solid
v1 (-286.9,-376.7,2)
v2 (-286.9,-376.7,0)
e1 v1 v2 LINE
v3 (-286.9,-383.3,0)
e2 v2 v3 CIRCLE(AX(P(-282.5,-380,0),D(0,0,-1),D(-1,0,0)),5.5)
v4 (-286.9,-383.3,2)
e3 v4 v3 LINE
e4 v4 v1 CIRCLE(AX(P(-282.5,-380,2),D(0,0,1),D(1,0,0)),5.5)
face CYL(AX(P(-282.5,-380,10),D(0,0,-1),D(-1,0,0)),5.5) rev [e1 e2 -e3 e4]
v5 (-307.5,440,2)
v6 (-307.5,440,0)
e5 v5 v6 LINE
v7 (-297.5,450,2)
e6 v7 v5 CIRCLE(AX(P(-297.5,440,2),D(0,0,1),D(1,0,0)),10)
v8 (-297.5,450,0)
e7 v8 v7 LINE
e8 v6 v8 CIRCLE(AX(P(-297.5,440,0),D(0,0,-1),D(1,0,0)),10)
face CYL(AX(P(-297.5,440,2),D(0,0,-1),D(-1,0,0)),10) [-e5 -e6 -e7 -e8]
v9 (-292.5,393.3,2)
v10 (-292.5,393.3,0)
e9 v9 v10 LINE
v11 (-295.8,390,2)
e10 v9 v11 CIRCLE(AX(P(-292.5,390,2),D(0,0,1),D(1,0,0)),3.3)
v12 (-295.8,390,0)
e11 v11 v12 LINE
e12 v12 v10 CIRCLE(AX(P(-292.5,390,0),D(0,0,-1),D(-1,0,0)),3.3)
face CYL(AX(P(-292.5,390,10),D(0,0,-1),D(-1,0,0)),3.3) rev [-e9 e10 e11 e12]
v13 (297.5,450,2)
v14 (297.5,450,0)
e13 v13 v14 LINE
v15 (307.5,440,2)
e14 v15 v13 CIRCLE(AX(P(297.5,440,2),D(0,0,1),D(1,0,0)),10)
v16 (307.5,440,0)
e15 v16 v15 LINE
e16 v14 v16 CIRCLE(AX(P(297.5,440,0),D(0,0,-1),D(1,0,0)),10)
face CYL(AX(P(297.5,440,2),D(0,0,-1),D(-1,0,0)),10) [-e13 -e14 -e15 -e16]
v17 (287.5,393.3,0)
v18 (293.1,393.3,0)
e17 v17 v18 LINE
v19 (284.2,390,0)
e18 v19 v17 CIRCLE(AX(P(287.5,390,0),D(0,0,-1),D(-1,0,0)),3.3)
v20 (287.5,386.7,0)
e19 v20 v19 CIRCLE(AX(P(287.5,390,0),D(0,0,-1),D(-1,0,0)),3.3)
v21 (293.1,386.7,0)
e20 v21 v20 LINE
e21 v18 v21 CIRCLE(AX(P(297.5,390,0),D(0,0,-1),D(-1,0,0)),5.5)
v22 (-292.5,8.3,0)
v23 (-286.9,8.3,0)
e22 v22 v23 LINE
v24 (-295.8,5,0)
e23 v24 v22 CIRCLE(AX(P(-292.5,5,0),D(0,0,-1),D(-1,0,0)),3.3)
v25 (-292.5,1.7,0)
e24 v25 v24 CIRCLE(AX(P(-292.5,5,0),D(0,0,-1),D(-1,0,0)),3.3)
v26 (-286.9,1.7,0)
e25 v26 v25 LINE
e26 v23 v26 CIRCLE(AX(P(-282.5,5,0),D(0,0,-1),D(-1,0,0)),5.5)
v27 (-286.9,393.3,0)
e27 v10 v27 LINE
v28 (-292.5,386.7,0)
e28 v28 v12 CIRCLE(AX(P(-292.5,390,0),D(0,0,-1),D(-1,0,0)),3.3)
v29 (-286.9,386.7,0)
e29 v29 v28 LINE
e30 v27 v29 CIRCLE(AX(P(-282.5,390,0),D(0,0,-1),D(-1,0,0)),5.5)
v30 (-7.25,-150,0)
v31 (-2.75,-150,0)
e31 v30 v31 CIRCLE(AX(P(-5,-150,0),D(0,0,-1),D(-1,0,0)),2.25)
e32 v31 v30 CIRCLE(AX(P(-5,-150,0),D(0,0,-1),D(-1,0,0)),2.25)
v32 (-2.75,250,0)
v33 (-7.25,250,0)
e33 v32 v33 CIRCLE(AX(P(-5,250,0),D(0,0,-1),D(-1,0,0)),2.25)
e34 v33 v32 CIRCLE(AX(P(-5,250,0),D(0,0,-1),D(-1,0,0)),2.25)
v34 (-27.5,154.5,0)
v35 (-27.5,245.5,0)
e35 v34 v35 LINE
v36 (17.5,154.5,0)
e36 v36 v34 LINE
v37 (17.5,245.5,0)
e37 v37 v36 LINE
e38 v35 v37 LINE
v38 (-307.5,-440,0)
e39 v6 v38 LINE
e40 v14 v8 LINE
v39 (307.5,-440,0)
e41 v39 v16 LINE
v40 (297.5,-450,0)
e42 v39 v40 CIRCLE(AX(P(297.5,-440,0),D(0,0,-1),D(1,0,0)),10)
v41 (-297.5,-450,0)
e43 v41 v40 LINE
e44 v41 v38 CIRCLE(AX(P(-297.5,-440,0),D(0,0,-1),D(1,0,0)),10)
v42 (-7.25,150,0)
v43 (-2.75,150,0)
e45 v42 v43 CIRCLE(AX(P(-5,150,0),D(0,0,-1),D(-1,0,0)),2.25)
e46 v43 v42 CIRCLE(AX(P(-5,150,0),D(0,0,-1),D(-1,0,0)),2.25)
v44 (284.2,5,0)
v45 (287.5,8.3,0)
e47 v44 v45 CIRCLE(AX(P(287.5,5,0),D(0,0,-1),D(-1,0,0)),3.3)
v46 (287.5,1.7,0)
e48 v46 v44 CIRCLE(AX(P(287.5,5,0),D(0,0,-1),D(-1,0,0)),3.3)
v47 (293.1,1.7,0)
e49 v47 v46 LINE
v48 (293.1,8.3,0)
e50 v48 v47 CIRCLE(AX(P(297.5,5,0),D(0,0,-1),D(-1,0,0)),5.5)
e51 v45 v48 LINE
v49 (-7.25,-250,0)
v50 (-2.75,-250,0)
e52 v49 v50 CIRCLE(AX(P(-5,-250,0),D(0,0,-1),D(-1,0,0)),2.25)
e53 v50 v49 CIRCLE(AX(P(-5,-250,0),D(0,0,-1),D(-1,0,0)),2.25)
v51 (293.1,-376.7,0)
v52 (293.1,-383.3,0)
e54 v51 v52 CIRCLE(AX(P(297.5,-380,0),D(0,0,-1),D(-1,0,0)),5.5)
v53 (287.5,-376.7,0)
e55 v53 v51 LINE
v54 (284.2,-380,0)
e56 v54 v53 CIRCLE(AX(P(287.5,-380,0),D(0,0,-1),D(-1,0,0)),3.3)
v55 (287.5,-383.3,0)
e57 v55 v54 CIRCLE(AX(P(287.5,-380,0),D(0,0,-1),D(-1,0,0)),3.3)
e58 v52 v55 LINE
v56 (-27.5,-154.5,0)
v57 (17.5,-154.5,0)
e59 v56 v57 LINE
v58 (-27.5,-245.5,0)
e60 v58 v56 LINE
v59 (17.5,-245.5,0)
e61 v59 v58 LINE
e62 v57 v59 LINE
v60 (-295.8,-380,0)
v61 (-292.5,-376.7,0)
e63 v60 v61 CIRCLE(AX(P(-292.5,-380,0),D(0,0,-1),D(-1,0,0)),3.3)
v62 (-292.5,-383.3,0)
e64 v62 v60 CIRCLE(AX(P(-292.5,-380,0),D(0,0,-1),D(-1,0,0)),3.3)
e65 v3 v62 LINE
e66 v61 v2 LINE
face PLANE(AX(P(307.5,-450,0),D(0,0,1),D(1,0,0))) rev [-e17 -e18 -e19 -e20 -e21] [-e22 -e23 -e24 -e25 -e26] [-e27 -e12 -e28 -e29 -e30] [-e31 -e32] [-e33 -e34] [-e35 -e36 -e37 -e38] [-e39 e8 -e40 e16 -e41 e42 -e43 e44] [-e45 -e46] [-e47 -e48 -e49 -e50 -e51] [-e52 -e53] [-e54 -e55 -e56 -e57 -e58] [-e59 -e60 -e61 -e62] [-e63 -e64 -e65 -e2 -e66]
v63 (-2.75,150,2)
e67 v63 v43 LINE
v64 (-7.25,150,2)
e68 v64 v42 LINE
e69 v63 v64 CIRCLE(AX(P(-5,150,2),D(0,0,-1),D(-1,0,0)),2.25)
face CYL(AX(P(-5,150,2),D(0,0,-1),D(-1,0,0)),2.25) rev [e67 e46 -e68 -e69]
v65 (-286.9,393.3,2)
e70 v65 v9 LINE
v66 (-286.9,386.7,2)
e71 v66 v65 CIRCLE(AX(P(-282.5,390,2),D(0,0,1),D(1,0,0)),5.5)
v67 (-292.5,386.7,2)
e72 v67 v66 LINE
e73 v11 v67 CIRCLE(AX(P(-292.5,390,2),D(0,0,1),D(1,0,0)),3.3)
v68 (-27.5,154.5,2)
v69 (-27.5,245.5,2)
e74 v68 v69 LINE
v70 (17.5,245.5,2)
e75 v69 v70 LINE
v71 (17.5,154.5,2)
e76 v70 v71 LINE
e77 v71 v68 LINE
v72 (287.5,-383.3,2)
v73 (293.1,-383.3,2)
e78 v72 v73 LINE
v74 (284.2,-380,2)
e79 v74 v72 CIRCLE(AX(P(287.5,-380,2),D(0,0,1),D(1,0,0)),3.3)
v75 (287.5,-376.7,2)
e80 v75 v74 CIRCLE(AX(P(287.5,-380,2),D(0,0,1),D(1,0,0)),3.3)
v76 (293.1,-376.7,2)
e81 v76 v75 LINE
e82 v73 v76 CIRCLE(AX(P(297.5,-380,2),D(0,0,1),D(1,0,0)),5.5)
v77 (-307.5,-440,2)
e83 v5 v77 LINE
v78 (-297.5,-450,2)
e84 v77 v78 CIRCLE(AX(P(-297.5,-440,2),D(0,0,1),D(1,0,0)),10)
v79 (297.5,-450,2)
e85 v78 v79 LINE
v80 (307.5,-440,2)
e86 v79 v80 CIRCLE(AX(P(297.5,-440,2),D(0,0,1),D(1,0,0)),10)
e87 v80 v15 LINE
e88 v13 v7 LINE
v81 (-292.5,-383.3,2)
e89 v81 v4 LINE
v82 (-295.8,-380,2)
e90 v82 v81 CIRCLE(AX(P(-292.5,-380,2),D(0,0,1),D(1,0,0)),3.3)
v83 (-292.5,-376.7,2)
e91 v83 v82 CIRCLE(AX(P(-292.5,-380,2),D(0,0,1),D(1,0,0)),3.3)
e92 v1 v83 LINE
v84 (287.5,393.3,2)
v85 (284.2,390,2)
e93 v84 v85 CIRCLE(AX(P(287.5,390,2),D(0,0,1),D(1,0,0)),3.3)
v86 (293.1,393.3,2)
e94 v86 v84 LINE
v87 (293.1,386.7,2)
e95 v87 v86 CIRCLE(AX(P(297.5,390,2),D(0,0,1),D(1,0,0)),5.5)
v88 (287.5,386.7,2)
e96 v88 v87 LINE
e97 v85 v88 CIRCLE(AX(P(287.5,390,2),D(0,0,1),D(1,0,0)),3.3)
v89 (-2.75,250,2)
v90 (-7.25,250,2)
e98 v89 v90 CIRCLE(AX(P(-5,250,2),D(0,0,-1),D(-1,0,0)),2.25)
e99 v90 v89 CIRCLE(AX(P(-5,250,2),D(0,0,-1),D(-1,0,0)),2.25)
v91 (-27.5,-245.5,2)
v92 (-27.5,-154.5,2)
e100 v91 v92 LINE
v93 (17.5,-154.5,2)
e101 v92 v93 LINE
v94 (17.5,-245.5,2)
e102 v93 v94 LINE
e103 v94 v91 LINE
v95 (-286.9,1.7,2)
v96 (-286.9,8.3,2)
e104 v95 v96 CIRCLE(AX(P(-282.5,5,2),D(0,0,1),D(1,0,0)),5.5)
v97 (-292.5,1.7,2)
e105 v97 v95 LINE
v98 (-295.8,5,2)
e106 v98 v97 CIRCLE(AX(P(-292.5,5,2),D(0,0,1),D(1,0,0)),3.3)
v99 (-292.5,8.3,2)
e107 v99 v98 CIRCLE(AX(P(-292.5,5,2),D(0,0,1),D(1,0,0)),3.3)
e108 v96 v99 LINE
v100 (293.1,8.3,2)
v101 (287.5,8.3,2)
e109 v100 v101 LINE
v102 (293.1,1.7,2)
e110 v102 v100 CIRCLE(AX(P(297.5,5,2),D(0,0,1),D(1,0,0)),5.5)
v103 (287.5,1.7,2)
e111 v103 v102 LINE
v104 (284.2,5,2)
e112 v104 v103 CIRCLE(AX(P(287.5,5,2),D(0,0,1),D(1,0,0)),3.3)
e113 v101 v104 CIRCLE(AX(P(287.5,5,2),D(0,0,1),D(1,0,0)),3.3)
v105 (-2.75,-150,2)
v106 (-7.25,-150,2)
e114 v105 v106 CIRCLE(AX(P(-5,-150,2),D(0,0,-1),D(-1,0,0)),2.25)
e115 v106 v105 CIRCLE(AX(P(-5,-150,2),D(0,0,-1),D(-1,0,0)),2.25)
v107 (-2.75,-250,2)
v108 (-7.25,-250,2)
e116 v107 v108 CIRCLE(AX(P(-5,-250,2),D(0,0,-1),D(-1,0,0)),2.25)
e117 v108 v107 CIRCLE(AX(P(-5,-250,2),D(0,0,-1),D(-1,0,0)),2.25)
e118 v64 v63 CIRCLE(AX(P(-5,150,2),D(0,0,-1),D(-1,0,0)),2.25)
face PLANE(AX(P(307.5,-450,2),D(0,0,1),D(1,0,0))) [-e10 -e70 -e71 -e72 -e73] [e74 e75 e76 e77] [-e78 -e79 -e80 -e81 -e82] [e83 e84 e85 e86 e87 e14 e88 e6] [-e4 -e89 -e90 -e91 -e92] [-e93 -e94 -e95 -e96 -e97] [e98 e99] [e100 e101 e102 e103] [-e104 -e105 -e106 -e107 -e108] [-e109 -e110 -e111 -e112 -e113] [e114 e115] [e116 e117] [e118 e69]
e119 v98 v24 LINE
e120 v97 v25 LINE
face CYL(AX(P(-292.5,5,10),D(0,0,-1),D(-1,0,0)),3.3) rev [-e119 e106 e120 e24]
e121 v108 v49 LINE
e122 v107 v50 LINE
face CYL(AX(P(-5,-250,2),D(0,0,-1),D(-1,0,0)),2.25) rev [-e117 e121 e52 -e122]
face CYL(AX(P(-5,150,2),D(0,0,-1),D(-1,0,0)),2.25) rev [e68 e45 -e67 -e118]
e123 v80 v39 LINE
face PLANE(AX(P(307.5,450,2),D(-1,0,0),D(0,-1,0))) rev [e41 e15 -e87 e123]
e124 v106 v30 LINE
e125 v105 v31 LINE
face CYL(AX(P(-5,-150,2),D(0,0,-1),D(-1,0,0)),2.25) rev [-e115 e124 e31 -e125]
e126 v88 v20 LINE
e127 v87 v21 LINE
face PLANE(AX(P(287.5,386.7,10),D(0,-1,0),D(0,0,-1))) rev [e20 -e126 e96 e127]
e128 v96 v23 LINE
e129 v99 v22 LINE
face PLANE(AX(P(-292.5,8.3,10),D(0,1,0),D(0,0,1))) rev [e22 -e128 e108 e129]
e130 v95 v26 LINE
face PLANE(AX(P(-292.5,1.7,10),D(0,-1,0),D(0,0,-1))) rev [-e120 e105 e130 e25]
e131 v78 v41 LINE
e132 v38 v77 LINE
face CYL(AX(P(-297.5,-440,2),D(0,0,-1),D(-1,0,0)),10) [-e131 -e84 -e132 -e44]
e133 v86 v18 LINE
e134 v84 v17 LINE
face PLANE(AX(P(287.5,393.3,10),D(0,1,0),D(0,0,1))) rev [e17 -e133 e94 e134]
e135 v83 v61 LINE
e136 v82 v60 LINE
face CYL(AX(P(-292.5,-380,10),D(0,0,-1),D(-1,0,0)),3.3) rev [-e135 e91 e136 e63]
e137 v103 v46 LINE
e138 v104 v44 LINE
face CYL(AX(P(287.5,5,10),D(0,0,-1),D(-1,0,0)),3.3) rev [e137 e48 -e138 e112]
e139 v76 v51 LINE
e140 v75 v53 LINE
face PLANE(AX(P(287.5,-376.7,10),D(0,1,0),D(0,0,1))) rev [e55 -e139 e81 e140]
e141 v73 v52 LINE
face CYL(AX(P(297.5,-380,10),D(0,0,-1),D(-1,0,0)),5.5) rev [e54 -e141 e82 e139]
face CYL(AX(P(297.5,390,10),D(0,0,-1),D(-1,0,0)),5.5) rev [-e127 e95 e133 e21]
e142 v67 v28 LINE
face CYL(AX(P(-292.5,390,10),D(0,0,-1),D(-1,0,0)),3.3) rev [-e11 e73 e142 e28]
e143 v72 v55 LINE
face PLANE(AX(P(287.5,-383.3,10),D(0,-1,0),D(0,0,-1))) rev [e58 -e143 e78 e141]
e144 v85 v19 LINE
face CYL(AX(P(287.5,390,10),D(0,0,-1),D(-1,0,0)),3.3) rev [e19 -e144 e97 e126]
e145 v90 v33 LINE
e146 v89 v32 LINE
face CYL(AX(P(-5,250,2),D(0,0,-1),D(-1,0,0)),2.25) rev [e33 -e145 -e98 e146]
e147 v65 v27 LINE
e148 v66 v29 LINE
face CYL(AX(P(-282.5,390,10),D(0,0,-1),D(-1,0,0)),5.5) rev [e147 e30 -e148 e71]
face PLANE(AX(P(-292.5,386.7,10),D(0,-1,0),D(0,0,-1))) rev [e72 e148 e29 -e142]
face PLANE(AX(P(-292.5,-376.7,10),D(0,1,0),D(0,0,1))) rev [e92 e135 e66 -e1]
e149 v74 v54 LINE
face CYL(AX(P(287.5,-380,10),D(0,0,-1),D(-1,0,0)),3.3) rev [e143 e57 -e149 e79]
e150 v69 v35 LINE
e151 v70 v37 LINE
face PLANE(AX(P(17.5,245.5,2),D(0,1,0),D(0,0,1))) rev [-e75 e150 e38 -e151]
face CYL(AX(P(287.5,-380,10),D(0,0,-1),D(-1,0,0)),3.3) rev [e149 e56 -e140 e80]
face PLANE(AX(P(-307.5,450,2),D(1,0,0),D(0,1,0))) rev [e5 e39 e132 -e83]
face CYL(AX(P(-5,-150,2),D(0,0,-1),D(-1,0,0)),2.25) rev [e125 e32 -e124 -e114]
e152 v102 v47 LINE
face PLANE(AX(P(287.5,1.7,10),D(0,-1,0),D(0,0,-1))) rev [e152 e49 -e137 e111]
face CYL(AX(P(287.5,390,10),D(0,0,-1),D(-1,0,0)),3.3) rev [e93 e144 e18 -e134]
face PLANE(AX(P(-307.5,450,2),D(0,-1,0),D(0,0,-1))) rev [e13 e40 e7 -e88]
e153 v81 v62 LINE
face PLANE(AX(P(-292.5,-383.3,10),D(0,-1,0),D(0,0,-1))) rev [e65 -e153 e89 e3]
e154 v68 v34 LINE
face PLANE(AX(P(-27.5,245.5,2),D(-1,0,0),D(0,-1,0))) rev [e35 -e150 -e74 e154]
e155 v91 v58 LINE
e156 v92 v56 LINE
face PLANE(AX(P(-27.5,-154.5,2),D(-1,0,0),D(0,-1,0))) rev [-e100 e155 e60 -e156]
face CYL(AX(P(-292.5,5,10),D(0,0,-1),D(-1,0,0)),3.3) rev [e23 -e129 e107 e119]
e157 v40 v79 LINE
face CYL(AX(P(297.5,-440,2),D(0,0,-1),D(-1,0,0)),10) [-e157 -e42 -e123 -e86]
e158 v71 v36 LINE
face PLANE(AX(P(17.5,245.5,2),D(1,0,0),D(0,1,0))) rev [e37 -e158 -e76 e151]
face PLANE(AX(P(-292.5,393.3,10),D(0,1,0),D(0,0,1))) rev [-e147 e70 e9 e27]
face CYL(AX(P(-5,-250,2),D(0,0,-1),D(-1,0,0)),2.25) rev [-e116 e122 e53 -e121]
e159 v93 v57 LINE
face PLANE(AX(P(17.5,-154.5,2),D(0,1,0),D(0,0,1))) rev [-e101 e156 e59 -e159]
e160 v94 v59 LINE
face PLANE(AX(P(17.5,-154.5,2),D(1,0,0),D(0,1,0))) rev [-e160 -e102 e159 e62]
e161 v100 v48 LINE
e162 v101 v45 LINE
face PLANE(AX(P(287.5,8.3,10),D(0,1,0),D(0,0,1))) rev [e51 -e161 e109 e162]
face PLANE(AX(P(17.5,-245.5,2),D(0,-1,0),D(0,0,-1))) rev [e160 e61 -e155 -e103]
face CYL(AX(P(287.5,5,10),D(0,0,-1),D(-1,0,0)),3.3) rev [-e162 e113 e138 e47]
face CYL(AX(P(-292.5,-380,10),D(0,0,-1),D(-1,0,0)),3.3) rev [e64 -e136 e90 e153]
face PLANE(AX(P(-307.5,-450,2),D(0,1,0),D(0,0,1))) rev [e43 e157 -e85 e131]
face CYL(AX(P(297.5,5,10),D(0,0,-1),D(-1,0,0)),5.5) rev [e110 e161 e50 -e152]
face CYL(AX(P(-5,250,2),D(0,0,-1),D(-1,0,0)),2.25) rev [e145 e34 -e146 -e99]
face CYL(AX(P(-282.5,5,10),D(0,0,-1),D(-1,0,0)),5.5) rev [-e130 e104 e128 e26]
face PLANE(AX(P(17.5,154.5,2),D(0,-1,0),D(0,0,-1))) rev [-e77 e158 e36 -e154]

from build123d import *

# Parameters (mm, degrees)
SKETCH1_W            = 615
SKETCH1_H            = 900
BOSS_EXTRUDE1_DEPTH  = 2
SKETCH7_W            = 45
SKETCH7_H            = 91
CUT_EXTRUDE4_DEPTH   = 546.03233849
SKETCH8_R            = 2.25
CUT_EXTRUDE5_DEPTH   = 546.03233849
FILLET3_R            = 10
CUT_EXTRUDE6_DEPTH   = 10
LPATTERN1_COUNT      = 3
LPATTERN1_PITCH      = 385
LPATTERN1_COUNT_DIR2 = 2
LPATTERN1_PITCH_DIR2 = 580


with BuildPart() as part:
    # Sketch1 → Boss-Extrude1 (new body)
    with BuildSketch(Plane.XY):
        Rectangle(SKETCH1_W, SKETCH1_H)
    extrude(amount=BOSS_EXTRUDE1_DEPTH)

    # Sketch7 → Cut-Extrude4 (cut, through all)
    with BuildSketch(Plane(origin=(0, 0, 0), x_dir=(-1, 0, 0), z_dir=(0, 0, -1))):
        with Locations((5, 200)):
            Rectangle(SKETCH7_W, SKETCH7_H)
        with Locations((5, -200)):
            Rectangle(SKETCH7_W, SKETCH7_H)
    extrude(amount=-CUT_EXTRUDE4_DEPTH, mode=Mode.SUBTRACT)

    # Sketch8 → Cut-Extrude5 (cut, through all)
    with BuildSketch(Plane(origin=(0, 0, 0), x_dir=(-1, 0, 0), z_dir=(0, 0, -1))):
        with Locations((5, 250)):
            Circle(SKETCH8_R)
        with Locations((5, 150)):
            Circle(SKETCH8_R)
        with Locations((5, -150)):
            Circle(SKETCH8_R)
        with Locations((5, -250)):
            Circle(SKETCH8_R)
    extrude(amount=-CUT_EXTRUDE5_DEPTH, mode=Mode.SUBTRACT)

    # Fillet3
    fillet3_edges = [part.edges().sort_by_distance(p)[0] for p in [
        (307.5, -450, 1),
        (-307.5, -450, 1),
        (-307.5, 450, 1),
        (307.5, 450, 1),
    ]]
    fillet(fillet3_edges, radius=FILLET3_R)

    # Sketch10 → Cut-Extrude6 (cut)
    with BuildSketch(Plane(origin=(0, 0, 0), x_dir=(-1, 0, 0), z_dir=(0, 0, -1))):
        with BuildLine():
            Line((292.5, 393.3), (286.9, 393.3))
            ThreePointArc((286.9, 393.3), (277, 390), (286.9, 386.7))
            Line((286.9, 386.7), (292.5, 386.7))
            ThreePointArc((292.5, 386.7), (295.8, 390), (292.5, 393.3))
        make_face()
    cut_extrude6 = extrude(amount=-CUT_EXTRUDE6_DEPTH, mode=Mode.SUBTRACT)

    # LPattern1: Cut-Extrude6 3 × 2
    with Locations(*[(j * LPATTERN1_PITCH_DIR2, -i * LPATTERN1_PITCH, 0) for i in range(LPATTERN1_COUNT) for j in range(LPATTERN1_COUNT_DIR2) if (i, j) != (0, 0)]):
        add(cut_extrude6, mode=Mode.SUBTRACT)


solid = part.part
